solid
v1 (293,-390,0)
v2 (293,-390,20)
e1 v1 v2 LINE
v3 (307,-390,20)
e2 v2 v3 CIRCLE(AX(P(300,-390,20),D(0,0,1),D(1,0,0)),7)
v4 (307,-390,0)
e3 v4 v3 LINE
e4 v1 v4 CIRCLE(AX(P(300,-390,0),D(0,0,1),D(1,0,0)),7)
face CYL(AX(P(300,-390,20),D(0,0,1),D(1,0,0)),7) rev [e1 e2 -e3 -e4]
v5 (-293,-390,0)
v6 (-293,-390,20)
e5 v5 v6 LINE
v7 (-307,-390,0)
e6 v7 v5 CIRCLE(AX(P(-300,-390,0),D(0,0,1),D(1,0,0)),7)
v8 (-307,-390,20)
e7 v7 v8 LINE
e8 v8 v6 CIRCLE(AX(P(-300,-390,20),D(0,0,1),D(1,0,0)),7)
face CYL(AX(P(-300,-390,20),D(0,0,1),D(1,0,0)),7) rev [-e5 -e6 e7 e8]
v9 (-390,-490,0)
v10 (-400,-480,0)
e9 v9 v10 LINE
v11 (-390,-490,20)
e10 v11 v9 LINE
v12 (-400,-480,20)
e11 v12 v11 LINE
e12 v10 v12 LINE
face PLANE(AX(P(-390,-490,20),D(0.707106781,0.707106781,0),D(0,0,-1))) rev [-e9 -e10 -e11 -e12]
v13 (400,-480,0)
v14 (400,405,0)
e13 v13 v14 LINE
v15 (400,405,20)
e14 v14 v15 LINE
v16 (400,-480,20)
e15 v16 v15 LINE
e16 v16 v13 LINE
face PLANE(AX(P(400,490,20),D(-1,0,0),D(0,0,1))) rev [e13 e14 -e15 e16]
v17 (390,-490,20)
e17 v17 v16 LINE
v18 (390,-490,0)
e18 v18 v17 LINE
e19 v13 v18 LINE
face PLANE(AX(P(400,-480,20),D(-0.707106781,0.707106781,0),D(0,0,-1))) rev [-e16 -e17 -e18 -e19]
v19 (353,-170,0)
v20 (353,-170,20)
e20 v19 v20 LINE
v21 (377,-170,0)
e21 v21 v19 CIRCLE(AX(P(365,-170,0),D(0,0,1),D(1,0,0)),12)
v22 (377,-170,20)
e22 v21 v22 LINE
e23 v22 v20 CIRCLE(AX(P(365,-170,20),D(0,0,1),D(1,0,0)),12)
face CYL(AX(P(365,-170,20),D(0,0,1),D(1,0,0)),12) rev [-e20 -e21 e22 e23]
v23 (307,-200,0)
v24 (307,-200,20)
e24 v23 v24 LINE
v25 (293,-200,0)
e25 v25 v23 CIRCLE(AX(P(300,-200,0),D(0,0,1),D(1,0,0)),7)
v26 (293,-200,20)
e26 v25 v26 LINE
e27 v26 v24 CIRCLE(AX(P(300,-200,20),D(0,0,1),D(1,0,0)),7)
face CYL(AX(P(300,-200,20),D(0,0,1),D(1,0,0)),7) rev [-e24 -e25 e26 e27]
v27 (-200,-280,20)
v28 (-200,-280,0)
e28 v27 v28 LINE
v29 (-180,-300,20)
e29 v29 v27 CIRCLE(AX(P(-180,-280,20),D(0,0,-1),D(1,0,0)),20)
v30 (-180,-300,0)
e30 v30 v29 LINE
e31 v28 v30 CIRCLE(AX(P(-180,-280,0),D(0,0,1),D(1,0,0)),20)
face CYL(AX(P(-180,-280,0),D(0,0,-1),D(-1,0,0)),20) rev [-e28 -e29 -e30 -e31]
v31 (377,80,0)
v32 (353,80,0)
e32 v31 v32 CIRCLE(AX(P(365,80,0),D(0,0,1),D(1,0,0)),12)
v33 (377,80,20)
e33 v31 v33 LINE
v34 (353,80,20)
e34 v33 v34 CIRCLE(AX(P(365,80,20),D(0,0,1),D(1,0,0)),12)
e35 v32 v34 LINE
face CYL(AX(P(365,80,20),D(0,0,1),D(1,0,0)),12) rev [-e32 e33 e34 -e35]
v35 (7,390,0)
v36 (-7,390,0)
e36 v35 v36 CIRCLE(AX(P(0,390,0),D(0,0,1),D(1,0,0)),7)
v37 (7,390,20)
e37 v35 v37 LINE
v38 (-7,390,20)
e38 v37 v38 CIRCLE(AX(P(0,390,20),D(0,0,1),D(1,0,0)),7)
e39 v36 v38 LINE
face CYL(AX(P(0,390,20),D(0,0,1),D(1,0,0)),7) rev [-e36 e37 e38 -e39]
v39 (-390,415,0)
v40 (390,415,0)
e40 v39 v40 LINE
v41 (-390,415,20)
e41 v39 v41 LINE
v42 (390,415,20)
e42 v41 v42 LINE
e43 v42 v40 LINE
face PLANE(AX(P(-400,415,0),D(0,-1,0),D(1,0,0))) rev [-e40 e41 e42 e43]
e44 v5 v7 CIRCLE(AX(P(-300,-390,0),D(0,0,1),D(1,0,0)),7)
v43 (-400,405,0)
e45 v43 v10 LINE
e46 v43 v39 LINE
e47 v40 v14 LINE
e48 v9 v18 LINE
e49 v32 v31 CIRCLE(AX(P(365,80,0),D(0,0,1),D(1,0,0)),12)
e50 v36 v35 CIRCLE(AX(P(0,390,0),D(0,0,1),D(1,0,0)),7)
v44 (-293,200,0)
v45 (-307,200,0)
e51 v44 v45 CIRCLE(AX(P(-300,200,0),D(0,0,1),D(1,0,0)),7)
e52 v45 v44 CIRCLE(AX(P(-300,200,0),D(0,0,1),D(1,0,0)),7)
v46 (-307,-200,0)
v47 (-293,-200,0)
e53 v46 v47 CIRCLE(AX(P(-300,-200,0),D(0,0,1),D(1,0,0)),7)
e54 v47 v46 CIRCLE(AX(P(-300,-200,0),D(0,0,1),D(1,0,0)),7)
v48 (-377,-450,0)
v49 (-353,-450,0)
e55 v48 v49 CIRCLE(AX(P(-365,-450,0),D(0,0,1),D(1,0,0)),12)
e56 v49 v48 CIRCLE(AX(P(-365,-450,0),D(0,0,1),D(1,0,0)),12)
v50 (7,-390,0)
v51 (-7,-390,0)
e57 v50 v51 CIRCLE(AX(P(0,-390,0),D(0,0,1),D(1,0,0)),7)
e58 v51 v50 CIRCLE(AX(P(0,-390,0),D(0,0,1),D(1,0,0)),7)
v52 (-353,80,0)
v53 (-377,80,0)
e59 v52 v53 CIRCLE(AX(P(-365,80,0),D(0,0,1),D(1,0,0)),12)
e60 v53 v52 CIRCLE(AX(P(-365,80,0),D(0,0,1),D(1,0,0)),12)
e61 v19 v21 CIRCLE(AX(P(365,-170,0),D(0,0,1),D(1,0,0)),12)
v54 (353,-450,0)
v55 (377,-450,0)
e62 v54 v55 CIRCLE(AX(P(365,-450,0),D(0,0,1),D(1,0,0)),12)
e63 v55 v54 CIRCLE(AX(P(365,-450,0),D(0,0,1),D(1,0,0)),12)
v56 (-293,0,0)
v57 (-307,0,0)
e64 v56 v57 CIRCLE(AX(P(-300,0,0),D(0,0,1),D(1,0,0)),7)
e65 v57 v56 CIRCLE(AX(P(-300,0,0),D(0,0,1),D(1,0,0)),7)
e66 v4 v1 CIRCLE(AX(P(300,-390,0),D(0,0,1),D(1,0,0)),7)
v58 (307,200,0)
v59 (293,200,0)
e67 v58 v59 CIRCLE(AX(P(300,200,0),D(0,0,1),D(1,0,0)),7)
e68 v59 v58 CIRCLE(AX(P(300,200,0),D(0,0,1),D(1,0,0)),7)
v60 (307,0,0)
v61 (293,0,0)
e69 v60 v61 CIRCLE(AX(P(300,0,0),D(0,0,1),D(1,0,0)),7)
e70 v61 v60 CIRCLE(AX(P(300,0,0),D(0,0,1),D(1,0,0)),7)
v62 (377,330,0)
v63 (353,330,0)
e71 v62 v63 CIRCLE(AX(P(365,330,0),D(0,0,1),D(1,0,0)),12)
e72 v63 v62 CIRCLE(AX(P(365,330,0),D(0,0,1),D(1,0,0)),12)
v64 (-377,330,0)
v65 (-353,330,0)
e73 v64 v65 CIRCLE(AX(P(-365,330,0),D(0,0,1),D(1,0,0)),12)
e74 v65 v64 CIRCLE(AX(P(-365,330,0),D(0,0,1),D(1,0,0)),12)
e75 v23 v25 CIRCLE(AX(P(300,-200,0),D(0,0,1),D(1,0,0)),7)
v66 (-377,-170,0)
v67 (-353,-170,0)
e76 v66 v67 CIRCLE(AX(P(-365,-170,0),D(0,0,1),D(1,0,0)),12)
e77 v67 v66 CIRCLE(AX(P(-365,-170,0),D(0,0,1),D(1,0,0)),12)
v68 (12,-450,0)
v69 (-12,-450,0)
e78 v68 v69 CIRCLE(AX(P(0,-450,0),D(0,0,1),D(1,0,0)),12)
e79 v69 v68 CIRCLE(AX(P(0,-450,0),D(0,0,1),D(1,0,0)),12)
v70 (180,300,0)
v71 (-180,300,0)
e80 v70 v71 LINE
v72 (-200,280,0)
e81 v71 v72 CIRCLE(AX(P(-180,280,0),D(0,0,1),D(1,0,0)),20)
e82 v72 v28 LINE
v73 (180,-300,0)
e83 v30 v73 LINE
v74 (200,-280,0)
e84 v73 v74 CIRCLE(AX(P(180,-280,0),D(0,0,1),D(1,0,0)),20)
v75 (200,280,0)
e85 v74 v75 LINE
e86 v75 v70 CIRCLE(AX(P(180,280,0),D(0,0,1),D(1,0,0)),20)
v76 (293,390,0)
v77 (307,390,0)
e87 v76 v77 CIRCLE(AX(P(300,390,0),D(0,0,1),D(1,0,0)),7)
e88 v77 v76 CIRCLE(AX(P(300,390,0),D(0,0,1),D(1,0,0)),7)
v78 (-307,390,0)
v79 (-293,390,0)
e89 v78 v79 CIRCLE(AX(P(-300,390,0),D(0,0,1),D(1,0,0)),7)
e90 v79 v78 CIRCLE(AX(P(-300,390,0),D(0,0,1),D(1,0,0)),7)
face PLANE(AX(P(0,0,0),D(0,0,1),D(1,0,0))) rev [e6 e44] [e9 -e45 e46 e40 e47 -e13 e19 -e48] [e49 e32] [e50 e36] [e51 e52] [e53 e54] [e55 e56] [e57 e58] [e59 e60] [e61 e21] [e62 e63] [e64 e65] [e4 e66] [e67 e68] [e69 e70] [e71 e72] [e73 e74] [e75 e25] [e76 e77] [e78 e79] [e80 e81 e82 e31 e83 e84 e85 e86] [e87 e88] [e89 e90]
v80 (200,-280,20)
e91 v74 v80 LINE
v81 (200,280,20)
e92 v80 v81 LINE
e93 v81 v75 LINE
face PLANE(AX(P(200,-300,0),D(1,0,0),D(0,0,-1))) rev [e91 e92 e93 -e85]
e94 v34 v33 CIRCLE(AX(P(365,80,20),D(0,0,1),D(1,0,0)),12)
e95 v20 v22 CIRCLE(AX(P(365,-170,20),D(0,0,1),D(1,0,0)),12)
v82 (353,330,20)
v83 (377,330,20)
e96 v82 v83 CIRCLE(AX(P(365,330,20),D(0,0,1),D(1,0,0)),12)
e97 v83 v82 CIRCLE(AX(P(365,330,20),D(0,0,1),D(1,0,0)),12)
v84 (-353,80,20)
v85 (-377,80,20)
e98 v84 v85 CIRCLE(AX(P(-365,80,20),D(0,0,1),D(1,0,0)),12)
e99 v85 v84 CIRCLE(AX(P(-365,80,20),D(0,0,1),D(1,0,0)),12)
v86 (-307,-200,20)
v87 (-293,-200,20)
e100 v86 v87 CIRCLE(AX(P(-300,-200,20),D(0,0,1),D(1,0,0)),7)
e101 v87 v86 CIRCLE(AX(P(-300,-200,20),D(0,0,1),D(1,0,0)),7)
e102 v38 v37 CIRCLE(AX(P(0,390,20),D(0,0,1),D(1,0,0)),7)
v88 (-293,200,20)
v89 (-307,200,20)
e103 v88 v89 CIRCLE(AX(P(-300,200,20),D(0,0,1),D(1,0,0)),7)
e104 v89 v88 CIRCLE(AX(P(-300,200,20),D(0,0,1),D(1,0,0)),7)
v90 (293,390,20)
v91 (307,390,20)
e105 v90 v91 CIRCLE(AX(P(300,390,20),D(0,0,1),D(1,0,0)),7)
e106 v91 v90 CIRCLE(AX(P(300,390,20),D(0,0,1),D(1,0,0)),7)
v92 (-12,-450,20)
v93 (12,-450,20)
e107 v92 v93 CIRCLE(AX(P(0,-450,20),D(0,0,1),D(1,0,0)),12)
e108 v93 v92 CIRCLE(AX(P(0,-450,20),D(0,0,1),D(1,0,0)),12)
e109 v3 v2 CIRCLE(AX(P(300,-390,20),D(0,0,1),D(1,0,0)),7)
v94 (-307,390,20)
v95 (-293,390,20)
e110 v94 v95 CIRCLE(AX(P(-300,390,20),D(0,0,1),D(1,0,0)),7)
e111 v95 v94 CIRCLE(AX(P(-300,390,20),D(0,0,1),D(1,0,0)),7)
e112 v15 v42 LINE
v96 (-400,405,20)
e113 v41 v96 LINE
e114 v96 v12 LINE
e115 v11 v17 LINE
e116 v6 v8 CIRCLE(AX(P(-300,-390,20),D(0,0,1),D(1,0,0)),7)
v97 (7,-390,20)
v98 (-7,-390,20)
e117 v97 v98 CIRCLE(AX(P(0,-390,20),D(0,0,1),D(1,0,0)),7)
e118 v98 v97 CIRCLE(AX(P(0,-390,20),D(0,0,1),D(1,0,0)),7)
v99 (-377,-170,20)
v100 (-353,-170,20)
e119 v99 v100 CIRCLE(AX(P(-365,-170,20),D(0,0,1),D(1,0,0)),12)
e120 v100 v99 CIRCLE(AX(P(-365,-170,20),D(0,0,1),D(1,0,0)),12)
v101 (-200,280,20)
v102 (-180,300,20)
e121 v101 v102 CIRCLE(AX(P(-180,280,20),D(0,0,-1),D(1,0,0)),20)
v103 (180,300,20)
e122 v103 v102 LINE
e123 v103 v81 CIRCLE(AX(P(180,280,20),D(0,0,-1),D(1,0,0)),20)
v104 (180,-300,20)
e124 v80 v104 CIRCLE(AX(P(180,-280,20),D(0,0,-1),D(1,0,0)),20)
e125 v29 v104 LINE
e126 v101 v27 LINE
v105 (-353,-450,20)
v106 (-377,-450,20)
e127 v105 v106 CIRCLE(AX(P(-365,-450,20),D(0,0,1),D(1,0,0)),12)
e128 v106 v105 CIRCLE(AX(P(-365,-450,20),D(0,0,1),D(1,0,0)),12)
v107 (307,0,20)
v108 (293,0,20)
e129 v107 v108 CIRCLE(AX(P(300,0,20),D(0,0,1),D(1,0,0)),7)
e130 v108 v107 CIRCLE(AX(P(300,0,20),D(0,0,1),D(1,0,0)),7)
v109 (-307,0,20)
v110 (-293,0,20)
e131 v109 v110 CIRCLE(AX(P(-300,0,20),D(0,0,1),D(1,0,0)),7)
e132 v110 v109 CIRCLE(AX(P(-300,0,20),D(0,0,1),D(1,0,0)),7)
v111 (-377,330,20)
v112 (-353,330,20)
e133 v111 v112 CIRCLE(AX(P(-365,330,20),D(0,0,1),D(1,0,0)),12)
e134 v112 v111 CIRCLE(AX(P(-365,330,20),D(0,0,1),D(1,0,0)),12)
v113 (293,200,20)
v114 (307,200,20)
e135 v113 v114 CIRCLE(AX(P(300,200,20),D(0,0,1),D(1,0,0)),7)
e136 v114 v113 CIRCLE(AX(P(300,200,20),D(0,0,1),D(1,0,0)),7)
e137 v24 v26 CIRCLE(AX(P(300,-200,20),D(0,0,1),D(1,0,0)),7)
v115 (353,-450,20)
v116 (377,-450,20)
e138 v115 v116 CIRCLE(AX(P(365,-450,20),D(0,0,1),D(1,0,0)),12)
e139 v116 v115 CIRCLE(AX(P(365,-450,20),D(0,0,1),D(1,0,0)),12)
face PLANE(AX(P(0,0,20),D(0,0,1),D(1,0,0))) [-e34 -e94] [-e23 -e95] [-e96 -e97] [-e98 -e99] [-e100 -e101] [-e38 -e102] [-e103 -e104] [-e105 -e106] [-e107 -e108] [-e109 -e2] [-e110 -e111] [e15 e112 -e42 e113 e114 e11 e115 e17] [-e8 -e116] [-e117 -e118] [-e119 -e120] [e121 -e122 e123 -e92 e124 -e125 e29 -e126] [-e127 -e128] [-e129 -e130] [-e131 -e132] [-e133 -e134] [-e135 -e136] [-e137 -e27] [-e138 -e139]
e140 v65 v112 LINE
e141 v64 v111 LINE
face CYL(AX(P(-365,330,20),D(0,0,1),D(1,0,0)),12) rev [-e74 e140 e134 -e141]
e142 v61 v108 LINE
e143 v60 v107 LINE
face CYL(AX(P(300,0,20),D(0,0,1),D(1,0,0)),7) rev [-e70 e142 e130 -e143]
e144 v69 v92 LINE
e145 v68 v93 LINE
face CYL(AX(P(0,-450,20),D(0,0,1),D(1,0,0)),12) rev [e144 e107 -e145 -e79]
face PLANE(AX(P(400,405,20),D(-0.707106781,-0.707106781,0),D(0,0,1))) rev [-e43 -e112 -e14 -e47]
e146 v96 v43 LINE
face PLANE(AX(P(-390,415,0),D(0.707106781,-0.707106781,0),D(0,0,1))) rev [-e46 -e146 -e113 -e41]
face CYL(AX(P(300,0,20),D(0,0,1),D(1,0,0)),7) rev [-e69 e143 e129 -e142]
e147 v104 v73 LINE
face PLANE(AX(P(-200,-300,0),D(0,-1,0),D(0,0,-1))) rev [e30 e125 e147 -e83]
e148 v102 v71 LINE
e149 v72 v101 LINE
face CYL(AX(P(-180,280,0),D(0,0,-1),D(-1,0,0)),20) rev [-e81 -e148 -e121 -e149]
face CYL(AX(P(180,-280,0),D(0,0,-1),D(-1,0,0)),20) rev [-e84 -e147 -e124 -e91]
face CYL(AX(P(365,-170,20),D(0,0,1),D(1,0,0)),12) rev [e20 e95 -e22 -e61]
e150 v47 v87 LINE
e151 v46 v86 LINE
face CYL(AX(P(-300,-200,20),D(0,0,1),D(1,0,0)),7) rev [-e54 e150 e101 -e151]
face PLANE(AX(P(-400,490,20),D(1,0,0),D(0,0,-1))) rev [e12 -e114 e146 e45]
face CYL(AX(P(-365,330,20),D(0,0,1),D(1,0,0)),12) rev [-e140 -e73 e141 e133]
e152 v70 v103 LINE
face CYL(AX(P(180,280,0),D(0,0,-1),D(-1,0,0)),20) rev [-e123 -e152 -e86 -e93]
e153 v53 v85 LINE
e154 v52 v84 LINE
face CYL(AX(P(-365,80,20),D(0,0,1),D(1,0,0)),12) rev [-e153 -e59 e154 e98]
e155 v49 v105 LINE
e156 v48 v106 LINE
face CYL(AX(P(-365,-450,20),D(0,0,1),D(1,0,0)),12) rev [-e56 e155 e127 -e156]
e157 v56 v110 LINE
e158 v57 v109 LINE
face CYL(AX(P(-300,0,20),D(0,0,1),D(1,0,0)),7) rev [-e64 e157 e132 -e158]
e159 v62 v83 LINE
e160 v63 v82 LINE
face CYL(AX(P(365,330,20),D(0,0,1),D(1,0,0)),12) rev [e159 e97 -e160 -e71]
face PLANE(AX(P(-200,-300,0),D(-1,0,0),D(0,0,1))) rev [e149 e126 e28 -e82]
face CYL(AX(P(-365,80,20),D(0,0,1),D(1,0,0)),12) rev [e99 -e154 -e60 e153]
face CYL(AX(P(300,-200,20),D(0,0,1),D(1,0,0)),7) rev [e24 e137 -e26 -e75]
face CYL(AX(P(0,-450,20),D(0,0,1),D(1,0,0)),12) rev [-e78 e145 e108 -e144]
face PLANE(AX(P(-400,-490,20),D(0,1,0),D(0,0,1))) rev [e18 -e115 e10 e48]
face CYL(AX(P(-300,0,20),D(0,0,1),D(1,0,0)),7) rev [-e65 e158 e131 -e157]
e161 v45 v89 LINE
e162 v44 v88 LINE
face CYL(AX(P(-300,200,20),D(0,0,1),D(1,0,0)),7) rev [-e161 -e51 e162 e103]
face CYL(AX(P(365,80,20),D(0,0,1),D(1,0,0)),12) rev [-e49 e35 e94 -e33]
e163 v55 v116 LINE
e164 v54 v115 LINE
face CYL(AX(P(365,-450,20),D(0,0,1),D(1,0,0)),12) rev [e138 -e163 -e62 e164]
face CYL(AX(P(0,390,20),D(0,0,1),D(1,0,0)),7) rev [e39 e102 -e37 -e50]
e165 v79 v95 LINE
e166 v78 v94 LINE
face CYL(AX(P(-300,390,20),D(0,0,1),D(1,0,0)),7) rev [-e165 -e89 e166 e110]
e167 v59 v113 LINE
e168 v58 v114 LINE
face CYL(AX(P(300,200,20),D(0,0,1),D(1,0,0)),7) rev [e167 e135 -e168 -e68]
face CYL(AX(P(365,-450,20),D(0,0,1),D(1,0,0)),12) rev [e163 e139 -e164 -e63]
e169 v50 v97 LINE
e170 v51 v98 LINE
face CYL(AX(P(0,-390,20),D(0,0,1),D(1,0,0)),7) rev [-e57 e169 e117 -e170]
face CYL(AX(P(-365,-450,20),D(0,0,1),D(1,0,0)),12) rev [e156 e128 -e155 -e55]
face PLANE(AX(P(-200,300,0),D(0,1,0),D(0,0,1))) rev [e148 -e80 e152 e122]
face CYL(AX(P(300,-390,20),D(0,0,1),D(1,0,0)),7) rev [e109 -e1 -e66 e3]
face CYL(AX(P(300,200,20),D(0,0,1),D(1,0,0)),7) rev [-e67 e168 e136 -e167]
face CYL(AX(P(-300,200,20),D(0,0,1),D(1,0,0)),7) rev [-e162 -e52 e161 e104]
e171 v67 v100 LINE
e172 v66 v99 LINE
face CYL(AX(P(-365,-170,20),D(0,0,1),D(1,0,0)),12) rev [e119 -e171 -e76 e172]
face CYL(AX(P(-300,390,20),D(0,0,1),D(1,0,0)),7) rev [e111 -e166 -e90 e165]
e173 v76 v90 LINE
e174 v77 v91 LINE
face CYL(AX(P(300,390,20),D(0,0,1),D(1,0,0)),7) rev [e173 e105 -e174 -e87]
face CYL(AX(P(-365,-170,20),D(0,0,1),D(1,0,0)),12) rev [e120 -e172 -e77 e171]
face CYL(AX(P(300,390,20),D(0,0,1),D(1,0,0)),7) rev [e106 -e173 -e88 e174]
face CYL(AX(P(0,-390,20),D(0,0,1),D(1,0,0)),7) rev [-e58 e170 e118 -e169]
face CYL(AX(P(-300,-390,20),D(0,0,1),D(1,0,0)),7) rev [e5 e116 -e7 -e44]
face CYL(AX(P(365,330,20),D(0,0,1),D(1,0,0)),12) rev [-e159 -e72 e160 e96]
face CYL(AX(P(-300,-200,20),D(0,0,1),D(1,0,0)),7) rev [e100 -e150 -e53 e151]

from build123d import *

# Parameters (mm, degrees)
SKETCH_1_W              = 800
SKETCH_1_H              = 980
EXTRUDE_1_DEPTH         = 20
HOLE_WIZARD_M16_1_D     = 14
HOLE_WIZARD_M16_1_DEPTH = 42
HOLE_WIZARD_M16_1_TIP   = 4.206024333
SKETCH_4_W              = 400
SKETCH_4_H              = 600
CUT_EXTRUDE_1_DEPTH     = 20
FILLET_1_R              = 20
SKETCH_10_W             = 800
SKETCH_10_H             = 75
CUT_EXTRUDE_3_DEPTH     = 633.850693292
HOLE_WIZARD_24_0_24_1_D = 24
CHAMFER_1_SIZE          = 10


with BuildPart() as part:
    # 草图1 → 凸台-拉伸1 (new body)
    with BuildSketch(Plane.XY):
        Rectangle(SKETCH_1_W, SKETCH_1_H)
    extrude(amount=EXTRUDE_1_DEPTH)

    # M16 螺纹孔1
    with Locations(Plane.XY.offset(20)):
        with Locations((300, 390), (-300, -390), (-300, 390), (300, -390), (-300, 0), (0, -390), (300, 0), (0, 390), (-300, 200), (300, 200), (-300, -200), (300, -200)):
            Hole(HOLE_WIZARD_M16_1_D / 2, depth=HOLE_WIZARD_M16_1_DEPTH)
            with Locations((0, 0, -(HOLE_WIZARD_M16_1_DEPTH + HOLE_WIZARD_M16_1_TIP / 2))):  # 118° drill point
                Cone(0, HOLE_WIZARD_M16_1_D / 2, HOLE_WIZARD_M16_1_TIP, mode=Mode.SUBTRACT)

    # 草图4 → 切除-拉伸1 (cut)
    with BuildSketch(Plane.XY.offset(20)):
        Rectangle(SKETCH_4_W, SKETCH_4_H)
    extrude(amount=-CUT_EXTRUDE_1_DEPTH, mode=Mode.SUBTRACT)

    # 圆角1
    fillet_1_edges = [part.edges().sort_by_distance(p)[0] for p in [
        (200, 300, 10),
        (200, -300, 10),
        (-200, -300, 10),
        (-200, 300, 10),
    ]]
    fillet(fillet_1_edges, radius=FILLET_1_R)

    # 草图10 → 切除-拉伸3 (cut, through all)
    with BuildSketch(Plane.XY.offset(20)):
        with Locations((0, 452.5)):
            Rectangle(SKETCH_10_W, SKETCH_10_H)
    extrude(amount=-CUT_EXTRUDE_3_DEPTH, mode=Mode.SUBTRACT)

    # Ø24.0 (24) 直径孔1 (through all)
    with Locations(Plane.XY.offset(20)):
        with Locations((365, 80), (365, -450), (-365, -450), (0, -450), (0, 450), (-365, 330), (365, 330), (-365, 80), (-365, -170), (365, -170)):
            Hole(HOLE_WIZARD_24_0_24_1_D / 2)

    # 倒角1
    chamfer_1_edges = [part.edges().sort_by_distance(p)[0] for p in [
        (-400, 415, 10),
        (400, 415, 10),
        (400, -490, 10),
        (-400, -490, 10),
    ]]
    chamfer(chamfer_1_edges, length=CHAMFER_1_SIZE)


solid = part.part
